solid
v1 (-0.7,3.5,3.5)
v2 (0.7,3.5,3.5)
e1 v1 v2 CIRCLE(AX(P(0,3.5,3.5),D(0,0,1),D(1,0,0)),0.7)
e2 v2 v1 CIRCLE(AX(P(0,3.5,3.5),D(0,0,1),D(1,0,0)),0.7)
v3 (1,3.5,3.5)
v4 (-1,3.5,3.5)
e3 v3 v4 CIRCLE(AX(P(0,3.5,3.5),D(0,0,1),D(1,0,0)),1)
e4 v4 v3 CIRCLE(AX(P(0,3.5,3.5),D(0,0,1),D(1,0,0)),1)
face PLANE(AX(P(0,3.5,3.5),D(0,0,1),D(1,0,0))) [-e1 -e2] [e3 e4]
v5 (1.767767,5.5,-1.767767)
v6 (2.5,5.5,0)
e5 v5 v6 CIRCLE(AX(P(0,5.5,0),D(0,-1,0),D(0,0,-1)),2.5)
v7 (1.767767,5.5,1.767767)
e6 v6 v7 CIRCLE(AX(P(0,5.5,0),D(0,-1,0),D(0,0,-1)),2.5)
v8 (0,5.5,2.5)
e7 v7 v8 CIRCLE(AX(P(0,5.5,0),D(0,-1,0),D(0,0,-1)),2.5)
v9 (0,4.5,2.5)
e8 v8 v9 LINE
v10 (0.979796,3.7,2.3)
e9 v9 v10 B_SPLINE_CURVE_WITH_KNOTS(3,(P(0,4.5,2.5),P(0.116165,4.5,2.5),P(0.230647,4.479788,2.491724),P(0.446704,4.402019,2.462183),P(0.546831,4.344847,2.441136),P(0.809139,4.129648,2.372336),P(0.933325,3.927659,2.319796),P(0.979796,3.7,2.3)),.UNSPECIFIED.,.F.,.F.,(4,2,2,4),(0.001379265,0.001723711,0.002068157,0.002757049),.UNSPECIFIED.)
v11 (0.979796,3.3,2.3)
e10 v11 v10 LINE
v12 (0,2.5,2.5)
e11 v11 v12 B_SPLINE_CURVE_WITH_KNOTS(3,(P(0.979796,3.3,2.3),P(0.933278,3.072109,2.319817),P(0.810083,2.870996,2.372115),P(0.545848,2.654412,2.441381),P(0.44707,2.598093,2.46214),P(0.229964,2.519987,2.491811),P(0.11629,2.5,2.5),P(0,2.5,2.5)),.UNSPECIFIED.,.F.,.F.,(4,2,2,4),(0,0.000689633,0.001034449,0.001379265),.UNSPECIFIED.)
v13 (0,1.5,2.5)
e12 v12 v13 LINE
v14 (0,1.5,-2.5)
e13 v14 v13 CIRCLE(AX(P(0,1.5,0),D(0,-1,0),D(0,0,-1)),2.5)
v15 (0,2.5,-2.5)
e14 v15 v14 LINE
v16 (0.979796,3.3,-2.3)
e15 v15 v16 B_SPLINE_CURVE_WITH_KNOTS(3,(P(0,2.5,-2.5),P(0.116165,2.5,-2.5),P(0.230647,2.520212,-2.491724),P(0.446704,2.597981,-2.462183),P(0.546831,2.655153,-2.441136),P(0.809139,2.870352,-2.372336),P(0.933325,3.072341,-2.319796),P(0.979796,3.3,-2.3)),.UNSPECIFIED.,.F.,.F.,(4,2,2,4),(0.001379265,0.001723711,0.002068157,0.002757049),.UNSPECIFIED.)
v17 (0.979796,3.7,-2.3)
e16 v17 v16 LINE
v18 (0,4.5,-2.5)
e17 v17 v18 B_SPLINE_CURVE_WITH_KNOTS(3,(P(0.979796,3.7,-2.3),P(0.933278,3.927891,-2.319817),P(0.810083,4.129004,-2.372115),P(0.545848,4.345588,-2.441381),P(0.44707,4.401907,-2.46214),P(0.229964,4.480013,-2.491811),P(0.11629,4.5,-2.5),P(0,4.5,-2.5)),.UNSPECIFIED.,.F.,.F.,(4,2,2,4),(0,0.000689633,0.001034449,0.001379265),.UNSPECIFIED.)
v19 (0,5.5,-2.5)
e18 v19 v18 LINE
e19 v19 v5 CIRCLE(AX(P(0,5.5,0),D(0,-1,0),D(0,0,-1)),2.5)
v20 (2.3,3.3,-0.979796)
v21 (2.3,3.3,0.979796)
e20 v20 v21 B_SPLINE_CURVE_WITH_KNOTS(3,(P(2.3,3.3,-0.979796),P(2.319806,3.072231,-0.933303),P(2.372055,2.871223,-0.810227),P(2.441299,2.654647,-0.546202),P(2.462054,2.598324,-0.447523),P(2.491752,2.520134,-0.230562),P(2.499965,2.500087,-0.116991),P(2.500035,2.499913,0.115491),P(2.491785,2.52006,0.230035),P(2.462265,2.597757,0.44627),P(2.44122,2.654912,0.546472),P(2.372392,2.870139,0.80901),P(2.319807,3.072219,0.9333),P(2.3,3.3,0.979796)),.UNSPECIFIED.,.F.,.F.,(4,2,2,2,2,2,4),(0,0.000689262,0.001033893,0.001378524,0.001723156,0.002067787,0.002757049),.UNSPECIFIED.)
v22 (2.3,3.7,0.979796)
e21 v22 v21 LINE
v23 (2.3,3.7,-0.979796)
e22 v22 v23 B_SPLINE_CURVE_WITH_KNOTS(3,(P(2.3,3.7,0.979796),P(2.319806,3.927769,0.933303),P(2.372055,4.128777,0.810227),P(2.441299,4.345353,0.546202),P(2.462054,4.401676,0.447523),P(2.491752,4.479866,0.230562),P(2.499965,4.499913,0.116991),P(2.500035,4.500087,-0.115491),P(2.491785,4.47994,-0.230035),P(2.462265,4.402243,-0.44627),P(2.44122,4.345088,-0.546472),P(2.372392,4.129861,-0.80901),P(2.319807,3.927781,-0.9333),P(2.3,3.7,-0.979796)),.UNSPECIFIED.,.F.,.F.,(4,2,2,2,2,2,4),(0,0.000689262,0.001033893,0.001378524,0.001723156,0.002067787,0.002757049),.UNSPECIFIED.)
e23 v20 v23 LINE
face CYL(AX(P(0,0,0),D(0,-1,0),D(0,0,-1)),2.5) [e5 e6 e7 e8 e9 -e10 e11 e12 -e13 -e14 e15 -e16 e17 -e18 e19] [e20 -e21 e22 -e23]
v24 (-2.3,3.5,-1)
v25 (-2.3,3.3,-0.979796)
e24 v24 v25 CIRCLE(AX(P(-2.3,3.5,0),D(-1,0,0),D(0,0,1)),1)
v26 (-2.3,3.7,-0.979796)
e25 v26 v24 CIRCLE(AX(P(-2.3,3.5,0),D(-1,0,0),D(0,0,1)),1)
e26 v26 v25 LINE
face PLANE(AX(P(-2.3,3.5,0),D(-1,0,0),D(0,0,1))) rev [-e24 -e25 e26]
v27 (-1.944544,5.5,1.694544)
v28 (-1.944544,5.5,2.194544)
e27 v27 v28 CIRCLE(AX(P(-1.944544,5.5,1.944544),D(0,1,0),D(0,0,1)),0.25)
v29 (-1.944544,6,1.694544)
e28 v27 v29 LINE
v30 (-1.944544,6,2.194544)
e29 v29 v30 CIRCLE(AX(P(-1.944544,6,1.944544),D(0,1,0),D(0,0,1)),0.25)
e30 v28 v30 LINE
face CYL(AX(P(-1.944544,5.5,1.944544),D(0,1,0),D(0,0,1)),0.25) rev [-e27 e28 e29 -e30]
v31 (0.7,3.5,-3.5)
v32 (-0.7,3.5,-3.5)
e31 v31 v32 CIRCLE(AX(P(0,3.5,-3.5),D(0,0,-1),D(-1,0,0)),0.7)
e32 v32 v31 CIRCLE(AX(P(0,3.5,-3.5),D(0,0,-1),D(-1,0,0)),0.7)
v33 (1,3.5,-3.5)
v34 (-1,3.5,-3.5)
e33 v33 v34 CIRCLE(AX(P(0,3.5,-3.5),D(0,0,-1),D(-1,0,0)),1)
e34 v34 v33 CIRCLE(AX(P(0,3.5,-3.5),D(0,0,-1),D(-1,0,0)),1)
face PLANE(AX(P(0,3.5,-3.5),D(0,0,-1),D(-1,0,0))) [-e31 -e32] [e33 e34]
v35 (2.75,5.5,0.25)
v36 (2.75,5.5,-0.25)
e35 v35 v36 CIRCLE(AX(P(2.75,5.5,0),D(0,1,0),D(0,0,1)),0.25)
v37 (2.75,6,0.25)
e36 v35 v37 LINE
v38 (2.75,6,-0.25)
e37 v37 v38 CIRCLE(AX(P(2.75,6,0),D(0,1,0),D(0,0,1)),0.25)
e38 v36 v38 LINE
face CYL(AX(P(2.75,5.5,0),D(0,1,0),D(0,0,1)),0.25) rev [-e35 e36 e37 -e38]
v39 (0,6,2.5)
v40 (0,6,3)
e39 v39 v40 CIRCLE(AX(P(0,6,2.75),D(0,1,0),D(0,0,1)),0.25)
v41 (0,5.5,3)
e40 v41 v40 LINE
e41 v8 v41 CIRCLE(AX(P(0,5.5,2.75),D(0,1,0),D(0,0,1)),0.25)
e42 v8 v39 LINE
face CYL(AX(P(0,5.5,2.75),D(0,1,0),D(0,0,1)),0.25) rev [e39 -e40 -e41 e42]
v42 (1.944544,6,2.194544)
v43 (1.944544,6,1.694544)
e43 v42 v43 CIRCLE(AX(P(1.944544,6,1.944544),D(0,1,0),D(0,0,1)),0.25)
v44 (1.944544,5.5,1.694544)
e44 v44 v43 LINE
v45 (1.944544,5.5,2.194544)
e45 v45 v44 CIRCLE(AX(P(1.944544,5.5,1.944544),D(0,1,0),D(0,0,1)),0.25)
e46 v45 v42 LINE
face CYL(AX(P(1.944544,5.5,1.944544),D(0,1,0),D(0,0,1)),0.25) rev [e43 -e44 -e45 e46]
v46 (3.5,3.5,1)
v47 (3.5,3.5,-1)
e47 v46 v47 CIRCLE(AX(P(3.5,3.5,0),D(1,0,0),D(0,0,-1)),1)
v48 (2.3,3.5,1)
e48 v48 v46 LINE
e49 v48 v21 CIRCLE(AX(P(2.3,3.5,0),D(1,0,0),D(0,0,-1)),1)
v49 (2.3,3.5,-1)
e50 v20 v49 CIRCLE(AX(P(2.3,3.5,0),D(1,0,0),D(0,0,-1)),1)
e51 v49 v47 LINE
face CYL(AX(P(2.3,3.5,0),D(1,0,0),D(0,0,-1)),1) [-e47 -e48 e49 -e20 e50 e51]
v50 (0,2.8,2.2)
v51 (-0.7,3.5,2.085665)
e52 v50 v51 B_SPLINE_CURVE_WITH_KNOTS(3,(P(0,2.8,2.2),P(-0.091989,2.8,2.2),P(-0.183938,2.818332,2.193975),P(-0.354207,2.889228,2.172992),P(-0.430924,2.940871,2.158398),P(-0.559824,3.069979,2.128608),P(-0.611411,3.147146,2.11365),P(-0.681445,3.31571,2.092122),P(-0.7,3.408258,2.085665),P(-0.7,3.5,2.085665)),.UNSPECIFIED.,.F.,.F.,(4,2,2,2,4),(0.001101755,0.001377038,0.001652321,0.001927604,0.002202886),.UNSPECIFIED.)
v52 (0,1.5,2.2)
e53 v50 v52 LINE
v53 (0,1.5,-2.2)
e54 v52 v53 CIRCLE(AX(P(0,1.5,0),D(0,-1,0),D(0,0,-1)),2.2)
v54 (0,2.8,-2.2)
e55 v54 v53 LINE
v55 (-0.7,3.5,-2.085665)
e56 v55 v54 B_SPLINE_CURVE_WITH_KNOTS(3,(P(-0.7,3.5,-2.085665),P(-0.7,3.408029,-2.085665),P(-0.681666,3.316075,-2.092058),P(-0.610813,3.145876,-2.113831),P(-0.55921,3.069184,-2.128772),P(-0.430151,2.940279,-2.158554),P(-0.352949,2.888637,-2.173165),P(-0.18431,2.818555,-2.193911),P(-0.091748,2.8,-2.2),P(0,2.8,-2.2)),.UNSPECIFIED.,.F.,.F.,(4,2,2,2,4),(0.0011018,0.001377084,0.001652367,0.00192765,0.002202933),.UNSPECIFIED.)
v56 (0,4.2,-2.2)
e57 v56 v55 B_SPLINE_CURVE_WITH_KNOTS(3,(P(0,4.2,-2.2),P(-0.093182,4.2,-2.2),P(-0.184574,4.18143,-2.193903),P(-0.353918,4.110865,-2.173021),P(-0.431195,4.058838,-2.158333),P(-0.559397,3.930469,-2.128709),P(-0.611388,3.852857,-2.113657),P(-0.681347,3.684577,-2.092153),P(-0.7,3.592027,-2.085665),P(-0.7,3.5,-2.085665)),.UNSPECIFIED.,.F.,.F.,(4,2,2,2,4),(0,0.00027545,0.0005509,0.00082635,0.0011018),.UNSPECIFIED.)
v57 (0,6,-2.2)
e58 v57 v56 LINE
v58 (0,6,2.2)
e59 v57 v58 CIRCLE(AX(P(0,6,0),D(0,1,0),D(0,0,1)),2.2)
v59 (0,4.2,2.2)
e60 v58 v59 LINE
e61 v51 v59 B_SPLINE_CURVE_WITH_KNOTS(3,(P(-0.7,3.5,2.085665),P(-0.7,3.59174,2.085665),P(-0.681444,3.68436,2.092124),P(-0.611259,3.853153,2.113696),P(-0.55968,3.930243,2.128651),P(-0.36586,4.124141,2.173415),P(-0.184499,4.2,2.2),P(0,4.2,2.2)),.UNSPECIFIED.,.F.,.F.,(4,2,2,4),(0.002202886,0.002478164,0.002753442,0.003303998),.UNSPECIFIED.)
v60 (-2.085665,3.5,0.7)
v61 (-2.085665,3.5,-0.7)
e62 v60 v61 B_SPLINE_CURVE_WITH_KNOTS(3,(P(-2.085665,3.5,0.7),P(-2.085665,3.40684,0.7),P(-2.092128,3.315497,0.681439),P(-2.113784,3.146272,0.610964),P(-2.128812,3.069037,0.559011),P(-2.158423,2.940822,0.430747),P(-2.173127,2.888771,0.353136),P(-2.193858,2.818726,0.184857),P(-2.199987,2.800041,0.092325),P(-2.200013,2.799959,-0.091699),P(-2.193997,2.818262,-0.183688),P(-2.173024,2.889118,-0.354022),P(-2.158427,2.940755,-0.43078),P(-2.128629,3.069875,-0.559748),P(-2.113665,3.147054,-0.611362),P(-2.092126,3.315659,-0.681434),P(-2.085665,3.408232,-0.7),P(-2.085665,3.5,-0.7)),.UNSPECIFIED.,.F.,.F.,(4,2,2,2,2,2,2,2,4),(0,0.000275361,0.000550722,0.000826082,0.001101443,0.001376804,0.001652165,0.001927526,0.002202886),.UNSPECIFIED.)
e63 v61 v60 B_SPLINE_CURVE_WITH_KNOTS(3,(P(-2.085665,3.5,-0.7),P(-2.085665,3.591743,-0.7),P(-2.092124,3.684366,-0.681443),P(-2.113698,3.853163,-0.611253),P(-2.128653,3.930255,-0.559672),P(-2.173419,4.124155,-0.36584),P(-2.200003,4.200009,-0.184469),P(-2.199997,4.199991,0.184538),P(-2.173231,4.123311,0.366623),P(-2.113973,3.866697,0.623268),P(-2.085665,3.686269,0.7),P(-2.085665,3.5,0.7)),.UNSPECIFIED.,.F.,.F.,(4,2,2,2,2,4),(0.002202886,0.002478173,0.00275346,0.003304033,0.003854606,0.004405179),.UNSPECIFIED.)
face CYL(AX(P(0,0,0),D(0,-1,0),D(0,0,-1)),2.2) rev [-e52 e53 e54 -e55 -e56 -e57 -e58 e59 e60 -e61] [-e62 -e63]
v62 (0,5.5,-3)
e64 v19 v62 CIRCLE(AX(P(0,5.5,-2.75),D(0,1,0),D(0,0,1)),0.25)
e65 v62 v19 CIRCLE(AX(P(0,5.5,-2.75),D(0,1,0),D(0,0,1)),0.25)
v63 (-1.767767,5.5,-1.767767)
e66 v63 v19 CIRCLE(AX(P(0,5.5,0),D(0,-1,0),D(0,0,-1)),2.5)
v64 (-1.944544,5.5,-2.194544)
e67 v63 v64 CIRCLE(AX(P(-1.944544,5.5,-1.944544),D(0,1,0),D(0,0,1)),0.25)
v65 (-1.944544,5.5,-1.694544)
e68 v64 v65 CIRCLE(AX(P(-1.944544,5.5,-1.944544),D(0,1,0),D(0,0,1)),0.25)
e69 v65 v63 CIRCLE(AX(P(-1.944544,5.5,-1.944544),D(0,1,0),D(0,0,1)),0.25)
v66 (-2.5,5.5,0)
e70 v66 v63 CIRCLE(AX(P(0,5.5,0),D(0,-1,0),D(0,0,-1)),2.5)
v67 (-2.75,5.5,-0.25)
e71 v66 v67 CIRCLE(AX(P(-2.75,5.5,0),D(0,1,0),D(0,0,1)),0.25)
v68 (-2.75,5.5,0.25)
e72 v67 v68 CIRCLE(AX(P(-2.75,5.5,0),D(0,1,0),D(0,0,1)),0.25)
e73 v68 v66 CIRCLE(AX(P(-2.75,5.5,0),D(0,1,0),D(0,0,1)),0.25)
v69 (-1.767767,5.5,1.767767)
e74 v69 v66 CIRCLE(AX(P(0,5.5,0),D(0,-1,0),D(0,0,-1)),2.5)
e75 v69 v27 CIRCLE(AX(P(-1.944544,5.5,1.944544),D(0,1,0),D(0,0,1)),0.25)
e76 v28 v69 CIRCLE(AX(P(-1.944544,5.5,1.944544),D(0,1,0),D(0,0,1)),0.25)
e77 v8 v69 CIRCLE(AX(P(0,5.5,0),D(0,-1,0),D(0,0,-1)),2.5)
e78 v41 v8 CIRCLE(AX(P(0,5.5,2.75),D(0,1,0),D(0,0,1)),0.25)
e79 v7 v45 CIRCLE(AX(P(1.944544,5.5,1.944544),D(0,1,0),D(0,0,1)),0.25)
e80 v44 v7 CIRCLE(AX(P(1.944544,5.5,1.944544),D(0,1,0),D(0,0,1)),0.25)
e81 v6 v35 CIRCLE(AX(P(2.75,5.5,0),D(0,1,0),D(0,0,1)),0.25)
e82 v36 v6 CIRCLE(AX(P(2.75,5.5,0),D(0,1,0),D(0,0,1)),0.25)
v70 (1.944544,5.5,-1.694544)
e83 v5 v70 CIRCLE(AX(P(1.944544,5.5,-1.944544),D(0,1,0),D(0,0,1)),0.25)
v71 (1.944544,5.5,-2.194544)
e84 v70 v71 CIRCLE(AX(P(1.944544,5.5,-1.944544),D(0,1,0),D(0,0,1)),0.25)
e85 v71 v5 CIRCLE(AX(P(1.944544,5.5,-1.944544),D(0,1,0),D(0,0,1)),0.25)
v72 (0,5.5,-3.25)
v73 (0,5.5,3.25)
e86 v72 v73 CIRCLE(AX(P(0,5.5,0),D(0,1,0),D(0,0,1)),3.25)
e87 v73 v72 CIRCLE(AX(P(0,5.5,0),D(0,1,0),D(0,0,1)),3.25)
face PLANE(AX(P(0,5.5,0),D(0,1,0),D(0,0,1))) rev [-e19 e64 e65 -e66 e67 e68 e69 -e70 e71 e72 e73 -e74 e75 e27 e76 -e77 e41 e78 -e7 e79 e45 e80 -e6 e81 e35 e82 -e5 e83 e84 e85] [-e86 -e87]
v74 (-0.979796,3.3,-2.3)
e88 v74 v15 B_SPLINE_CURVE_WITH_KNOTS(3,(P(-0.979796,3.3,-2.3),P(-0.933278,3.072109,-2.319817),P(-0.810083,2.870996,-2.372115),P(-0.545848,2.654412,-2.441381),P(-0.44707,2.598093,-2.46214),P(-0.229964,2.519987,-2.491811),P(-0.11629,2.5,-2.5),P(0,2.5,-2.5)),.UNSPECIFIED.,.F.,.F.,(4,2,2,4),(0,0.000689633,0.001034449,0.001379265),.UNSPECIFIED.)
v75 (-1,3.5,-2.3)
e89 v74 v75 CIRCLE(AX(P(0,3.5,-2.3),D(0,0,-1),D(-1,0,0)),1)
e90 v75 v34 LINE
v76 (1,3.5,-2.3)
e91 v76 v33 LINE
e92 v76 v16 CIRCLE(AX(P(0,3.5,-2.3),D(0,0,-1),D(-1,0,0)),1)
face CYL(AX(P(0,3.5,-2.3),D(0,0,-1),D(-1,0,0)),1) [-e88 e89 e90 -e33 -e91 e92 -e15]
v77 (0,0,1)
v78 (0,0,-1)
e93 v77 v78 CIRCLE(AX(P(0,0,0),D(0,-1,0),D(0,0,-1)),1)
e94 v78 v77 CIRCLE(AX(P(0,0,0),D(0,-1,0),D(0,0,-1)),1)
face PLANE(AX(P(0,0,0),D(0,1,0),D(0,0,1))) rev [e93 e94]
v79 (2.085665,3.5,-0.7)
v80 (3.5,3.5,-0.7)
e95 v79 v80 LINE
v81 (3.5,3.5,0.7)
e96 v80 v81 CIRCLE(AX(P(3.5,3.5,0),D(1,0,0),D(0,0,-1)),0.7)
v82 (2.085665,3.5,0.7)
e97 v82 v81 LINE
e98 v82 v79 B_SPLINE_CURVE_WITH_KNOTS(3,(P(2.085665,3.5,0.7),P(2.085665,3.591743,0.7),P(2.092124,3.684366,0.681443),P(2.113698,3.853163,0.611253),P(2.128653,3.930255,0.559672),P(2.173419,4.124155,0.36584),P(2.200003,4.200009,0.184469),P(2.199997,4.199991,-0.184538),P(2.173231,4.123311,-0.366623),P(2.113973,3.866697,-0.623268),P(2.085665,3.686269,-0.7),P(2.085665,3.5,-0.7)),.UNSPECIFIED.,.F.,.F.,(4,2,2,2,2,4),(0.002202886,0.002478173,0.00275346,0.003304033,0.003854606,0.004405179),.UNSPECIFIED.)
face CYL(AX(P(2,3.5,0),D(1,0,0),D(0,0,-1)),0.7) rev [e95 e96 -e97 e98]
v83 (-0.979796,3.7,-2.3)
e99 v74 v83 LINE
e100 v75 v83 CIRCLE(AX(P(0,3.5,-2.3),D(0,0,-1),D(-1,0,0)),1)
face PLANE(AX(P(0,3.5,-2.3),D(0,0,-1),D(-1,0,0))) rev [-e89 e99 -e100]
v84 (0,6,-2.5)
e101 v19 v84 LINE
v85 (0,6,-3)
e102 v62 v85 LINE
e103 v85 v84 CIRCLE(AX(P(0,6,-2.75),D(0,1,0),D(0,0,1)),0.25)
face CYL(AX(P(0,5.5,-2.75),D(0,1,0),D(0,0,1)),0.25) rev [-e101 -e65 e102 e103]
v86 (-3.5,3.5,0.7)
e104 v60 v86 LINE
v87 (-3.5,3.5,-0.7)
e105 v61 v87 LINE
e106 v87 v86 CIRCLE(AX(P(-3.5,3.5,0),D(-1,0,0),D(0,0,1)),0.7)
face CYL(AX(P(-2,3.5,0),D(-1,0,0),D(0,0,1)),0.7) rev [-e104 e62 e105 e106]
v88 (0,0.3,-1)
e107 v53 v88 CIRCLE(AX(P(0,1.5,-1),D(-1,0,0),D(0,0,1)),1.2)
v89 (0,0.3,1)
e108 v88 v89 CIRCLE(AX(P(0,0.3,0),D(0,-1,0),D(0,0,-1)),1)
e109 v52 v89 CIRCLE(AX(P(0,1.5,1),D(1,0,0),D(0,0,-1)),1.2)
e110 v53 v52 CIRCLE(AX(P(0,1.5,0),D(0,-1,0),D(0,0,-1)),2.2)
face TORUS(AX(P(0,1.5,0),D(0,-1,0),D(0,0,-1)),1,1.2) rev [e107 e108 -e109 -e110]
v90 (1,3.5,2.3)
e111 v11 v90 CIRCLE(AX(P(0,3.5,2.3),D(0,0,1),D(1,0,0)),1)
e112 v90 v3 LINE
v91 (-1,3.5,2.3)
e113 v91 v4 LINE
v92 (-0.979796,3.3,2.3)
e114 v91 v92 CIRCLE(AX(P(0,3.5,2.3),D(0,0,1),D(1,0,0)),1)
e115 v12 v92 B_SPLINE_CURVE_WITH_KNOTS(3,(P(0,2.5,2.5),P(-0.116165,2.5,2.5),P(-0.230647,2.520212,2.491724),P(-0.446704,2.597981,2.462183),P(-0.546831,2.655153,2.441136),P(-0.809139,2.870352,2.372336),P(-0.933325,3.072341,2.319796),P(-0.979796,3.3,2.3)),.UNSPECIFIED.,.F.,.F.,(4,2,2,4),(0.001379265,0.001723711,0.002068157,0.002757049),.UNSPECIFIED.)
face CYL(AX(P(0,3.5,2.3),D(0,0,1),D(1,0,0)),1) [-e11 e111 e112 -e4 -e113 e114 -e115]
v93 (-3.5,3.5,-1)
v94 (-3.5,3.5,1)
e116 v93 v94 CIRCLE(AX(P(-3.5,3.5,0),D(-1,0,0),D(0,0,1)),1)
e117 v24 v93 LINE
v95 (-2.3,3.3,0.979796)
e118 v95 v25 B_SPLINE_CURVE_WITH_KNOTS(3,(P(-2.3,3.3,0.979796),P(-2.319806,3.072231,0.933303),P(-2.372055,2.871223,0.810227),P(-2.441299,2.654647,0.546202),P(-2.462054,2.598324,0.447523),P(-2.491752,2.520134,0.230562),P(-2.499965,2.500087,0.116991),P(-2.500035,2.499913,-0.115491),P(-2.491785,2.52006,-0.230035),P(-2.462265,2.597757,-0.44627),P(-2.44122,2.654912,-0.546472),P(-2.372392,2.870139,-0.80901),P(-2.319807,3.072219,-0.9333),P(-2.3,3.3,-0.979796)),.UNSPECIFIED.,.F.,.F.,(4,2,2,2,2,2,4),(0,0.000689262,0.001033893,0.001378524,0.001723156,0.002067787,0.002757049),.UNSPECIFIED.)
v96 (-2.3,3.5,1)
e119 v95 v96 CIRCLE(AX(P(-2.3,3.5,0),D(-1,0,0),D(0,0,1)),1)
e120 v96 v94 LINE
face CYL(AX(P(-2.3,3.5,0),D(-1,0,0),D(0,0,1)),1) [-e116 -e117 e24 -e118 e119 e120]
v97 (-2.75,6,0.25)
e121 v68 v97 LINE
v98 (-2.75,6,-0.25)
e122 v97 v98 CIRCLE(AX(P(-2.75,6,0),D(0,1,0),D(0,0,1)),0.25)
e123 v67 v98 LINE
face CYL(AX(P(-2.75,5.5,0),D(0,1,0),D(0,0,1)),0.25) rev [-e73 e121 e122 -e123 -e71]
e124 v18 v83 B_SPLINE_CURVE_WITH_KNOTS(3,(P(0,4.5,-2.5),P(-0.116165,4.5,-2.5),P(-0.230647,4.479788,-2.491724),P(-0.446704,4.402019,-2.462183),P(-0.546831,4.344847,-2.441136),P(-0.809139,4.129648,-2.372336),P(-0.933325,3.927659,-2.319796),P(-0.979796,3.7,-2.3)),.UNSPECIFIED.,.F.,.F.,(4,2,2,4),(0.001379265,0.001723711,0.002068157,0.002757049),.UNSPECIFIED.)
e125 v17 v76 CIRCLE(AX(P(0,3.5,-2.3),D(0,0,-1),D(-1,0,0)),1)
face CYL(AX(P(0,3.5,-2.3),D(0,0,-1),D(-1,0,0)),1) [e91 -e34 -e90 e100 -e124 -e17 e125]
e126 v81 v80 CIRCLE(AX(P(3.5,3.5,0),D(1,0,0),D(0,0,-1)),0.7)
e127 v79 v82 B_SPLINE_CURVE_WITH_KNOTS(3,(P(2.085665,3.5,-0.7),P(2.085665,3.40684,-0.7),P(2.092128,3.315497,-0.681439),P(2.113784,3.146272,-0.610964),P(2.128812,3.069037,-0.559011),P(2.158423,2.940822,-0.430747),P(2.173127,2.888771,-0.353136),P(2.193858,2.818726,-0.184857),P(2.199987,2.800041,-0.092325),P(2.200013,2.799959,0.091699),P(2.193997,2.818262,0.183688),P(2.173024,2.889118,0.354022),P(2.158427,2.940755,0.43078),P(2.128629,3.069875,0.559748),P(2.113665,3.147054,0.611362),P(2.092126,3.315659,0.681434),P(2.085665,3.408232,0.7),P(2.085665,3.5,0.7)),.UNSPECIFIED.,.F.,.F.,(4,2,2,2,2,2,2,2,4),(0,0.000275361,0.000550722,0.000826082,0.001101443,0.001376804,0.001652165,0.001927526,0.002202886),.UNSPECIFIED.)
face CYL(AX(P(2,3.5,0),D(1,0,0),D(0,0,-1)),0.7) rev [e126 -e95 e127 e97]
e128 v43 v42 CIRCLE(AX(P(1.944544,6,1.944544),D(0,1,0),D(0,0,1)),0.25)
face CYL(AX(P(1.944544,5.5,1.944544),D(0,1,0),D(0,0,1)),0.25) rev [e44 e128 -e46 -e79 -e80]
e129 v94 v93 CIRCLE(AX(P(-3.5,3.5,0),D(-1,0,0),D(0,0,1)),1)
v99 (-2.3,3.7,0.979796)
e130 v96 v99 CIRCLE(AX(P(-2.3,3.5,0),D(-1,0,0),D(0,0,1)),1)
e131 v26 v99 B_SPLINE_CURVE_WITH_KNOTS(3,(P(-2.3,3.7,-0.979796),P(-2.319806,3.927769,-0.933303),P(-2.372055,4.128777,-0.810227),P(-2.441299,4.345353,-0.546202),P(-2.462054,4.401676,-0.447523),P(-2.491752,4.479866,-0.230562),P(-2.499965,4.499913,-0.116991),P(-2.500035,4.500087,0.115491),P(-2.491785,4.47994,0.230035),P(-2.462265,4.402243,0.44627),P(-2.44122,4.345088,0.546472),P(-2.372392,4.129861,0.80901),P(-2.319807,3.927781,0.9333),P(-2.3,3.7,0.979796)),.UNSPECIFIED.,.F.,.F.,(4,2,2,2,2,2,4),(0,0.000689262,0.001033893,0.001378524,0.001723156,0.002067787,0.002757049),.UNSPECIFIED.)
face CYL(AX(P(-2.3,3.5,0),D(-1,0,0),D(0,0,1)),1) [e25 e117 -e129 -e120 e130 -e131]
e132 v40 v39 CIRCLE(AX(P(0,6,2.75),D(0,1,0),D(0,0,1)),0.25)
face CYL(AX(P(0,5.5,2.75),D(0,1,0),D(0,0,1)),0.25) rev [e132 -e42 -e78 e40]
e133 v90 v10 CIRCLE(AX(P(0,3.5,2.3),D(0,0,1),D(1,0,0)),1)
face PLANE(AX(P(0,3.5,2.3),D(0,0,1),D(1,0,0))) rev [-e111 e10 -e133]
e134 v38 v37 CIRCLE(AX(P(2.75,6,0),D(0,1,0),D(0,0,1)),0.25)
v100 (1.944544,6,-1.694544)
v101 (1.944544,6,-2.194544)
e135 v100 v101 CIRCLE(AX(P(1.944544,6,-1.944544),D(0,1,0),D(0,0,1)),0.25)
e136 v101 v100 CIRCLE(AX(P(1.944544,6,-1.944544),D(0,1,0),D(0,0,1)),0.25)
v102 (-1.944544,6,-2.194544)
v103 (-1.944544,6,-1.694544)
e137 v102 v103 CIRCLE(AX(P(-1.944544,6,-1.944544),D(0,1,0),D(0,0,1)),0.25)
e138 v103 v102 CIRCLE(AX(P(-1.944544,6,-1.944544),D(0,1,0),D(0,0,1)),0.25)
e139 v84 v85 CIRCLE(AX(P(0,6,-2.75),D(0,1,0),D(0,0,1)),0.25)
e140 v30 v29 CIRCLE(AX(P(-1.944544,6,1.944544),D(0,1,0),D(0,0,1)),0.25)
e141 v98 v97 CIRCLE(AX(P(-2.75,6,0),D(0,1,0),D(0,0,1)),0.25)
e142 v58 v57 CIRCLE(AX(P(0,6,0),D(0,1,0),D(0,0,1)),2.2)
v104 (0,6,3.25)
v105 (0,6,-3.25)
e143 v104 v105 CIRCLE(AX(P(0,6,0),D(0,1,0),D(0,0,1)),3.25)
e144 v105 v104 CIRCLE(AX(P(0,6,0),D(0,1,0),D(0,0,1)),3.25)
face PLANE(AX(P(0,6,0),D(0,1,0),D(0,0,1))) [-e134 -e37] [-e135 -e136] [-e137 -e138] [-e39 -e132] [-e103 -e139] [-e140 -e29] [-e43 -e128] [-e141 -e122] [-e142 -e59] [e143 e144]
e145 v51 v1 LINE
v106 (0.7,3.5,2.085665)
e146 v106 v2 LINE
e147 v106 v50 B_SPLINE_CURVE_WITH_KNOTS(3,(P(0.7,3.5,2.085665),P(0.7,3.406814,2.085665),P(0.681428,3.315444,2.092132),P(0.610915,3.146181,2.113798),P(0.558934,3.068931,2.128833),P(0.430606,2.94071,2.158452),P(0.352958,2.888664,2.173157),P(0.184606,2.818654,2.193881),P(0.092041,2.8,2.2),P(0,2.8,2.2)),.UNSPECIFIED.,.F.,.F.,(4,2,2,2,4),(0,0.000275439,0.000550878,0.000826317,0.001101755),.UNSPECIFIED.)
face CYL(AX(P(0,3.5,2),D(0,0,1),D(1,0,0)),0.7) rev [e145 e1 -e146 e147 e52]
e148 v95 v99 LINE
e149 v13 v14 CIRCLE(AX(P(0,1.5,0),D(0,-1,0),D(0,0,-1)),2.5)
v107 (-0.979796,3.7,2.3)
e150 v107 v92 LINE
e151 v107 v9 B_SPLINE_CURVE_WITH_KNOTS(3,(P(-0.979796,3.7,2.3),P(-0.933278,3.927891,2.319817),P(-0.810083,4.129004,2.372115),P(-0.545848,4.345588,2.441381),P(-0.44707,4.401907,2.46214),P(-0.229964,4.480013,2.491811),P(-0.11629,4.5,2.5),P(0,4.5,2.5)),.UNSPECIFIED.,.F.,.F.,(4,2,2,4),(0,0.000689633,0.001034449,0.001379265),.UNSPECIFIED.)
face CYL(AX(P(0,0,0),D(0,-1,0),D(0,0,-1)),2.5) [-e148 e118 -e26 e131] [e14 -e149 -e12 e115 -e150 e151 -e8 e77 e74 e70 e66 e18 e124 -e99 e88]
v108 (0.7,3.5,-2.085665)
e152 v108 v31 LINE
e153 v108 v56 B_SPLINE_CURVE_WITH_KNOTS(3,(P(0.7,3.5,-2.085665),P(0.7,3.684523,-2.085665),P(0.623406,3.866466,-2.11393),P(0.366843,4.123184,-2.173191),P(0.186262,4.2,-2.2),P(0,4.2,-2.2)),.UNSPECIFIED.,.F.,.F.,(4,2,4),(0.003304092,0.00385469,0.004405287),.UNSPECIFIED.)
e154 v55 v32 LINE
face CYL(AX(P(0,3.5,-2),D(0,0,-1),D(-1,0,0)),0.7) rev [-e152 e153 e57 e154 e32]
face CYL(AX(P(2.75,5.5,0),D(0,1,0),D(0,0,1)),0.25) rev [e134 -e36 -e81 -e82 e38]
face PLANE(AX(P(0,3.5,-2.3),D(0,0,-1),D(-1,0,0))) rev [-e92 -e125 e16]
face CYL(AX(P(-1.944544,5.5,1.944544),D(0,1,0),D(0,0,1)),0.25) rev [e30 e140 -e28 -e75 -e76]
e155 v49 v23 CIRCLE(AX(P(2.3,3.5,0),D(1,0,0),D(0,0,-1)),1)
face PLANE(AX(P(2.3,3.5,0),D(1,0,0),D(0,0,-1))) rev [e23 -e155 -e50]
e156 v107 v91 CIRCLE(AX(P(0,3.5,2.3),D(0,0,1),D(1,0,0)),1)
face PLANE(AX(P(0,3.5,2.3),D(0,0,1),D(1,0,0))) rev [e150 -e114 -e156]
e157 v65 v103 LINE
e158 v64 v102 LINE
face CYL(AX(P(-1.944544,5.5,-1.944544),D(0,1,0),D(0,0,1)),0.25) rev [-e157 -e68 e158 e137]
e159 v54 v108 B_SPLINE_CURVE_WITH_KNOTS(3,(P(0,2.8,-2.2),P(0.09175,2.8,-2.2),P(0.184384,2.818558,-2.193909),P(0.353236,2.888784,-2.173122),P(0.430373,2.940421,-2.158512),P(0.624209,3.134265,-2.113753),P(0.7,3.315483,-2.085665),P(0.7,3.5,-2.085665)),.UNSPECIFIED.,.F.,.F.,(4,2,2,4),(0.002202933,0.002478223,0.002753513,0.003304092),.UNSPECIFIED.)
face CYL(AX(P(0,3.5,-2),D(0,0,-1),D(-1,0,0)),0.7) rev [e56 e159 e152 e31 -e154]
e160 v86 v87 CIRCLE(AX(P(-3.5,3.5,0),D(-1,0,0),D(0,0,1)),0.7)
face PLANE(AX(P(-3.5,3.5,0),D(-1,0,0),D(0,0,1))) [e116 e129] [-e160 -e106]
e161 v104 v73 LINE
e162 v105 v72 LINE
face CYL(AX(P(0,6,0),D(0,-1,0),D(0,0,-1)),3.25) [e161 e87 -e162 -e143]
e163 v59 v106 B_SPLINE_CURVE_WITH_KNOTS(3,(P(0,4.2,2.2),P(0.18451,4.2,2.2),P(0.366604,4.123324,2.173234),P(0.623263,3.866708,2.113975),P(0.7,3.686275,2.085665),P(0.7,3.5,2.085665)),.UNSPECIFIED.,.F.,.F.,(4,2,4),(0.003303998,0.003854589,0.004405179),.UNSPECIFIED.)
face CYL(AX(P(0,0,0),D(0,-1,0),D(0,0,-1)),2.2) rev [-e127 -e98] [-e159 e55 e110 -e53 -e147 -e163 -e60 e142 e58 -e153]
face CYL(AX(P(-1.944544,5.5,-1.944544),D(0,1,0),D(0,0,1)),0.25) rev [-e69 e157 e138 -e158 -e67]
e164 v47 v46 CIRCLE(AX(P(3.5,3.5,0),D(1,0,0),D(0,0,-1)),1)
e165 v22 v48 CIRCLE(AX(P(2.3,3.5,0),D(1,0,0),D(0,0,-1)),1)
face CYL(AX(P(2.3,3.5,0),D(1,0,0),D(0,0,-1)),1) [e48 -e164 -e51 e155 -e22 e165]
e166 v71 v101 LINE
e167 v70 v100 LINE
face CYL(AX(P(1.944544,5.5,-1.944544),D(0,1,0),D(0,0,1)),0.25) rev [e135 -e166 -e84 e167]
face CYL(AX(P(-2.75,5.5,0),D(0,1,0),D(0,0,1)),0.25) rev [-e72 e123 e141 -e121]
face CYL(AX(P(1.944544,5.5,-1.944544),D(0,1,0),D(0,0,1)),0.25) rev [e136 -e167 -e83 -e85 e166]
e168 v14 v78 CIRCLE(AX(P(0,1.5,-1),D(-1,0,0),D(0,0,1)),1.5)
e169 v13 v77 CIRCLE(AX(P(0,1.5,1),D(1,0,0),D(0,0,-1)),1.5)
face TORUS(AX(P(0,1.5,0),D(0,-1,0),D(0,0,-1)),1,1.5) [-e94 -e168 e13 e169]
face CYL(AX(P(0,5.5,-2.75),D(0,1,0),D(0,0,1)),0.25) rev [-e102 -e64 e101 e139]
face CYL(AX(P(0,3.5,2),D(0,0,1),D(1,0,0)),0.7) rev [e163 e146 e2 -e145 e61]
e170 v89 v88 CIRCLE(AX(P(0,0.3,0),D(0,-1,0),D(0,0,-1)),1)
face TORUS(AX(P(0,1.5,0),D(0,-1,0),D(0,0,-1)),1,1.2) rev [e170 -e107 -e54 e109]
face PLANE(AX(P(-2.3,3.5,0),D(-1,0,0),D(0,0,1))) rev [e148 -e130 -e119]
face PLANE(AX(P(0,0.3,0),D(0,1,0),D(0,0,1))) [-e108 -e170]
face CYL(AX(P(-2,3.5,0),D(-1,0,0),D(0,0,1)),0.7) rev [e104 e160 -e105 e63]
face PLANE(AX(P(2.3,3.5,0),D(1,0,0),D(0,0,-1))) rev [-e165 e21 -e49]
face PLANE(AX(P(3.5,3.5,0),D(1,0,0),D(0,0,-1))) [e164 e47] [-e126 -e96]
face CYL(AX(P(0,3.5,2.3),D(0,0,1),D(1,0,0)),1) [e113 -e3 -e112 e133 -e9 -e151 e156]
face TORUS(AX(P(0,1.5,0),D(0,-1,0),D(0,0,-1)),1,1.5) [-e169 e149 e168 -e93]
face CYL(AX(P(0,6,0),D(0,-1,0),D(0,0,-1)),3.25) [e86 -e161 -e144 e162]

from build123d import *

# Parameters (mm, degrees)
BODY_SHELL_0_3_T            = -0.3
FLANGE_SKETCH_6_5_R         = 3.25
FLANGE_DEPTH                = 0.5
FLANGE_START                = -0.5
FLANGE_BORE_SKETCH_R        = 2.2
FLANGE_BORE_DEPTH           = 0.5
FLANGE_BOLT_HOLES_SKETCH_R  = 0.25
FLANGE_BOLT_HOLES_8X_DEPTH  = 0.5
SIDE_PORT_BOSS_SKETCH_2_R   = 1
SIDE_PORT_BOSS_DEPTH        = 1.2
SIDE_PORT_BORE_SKETCH_1_4_R = 0.7
SIDE_PORT_BORE_1_4_DEPTH    = 1.5
SIDE_PORT_PATTERN_4X_COUNT  = 4


with BuildPart() as part:
    # Body Profile Sketch → Body Revolve (revolve)
    with BuildSketch(Plane.XY, mode=Mode.PRIVATE) as body_revolve_sk:
        with BuildLine():
            Line((0, 0), (0, 5.5))
            Line((0, 5.5), (-2.5, 5.5))
            Line((-2.5, 5.5), (-2.5, 1.5))
            ThreePointArc((-2.5, 1.5), (-2.060660172, 0.439339828), (-1, 0))
            Line((-1, 0), (0, 0))
        make_face()
    revolve(body_revolve_sk.sketch.rotate(Axis((0, 0, 0), (0, 1, 0)), 270), axis=Axis((0, 0, 0), (0, 1, 0)))

    # Body Shell 0.3
    body_shell_0_3_openings = [part.faces().sort_by_distance(p)[0] for p in [
        (0, 5.5, 0),
    ]]
    offset(amount=BODY_SHELL_0_3_T, openings=body_shell_0_3_openings, kind=Kind.INTERSECTION)

    # Flange Sketch Ø6.5 → Flange (add)
    with BuildSketch(Plane(origin=(0, 5.5, 0), x_dir=(1, 0, 0), z_dir=(0, 1, 0))):
        with Locations(Location((0, 0, 0), (0, 0, 270))):
            Circle(FLANGE_SKETCH_6_5_R)
    extrude(amount=FLANGE_DEPTH)

    # Flange Bore Sketch → Flange Bore (cut)
    with BuildSketch(Plane(origin=(0, 6, 0), x_dir=(1, 0, 0), z_dir=(0, 1, 0)).offset(FLANGE_START)):
        with Locations(Location((0, 0, 0), (0, 0, 90))):
            Circle(FLANGE_BORE_SKETCH_R)
    extrude(amount=FLANGE_BORE_DEPTH, mode=Mode.SUBTRACT)

    # Flange Bolt Holes Sketch → Flange Bolt Holes 8x (cut)
    with BuildSketch(Plane(origin=(0, 6, 0), x_dir=(1, 0, 0), z_dir=(0, 1, 0))):
        with Locations(Location((0, 2.75, 0), (0, 0, 270))):
            Circle(FLANGE_BOLT_HOLES_SKETCH_R)
        with Locations(Location((1.944543648, 1.944543648, 0), (0, 0, 270))):
            Circle(FLANGE_BOLT_HOLES_SKETCH_R)
        with Locations(Location((2.75, 0, 0), (0, 0, 270))):
            Circle(FLANGE_BOLT_HOLES_SKETCH_R)
        with Locations(Location((1.944543648, -1.944543648, 0), (0, 0, 270))):
            Circle(FLANGE_BOLT_HOLES_SKETCH_R)
        with Locations(Location((0, -2.75, 0), (0, 0, 270))):
            Circle(FLANGE_BOLT_HOLES_SKETCH_R)
        with Locations(Location((-1.944543648, -1.944543648, 0), (0, 0, 270))):
            Circle(FLANGE_BOLT_HOLES_SKETCH_R)
        with Locations(Location((-2.75, 0, 0), (0, 0, 270))):
            Circle(FLANGE_BOLT_HOLES_SKETCH_R)
        with Locations(Location((-1.944543648, 1.944543648, 0), (0, 0, 270))):
            Circle(FLANGE_BOLT_HOLES_SKETCH_R)
    extrude(amount=-FLANGE_BOLT_HOLES_8X_DEPTH, mode=Mode.SUBTRACT)

    # Side Port Boss Sketch Ø2 → Side Port Boss (add)
    with BuildSketch(Plane.XY.offset(3.5)):
        with Locations((0, 3.5)):
            Circle(SIDE_PORT_BOSS_SKETCH_2_R)
    side_port_boss = extrude(amount=-SIDE_PORT_BOSS_DEPTH)

    # Side Port Bore Sketch Ø1.4 → Side Port Bore Ø1.4 (cut)
    with BuildSketch(Plane.XY.offset(3.5)):
        with Locations((0, 3.5)):
            Circle(SIDE_PORT_BORE_SKETCH_1_4_R)
    side_port_bore_1_4 = extrude(amount=-SIDE_PORT_BORE_1_4_DEPTH, mode=Mode.SUBTRACT)

    # Side Port Pattern 4x: Side Port Boss, Side Port Bore Ø1.4 ×4 about axis
    side_port_pattern_4x_axis = Axis((0, 0, 0), (0, 1, 0))
    add([side_port_boss.rotate(side_port_pattern_4x_axis, i * 360 / SIDE_PORT_PATTERN_4X_COUNT) for i in range(1, SIDE_PORT_PATTERN_4X_COUNT)])
    add([side_port_bore_1_4.rotate(side_port_pattern_4x_axis, i * 360 / SIDE_PORT_PATTERN_4X_COUNT) for i in range(1, SIDE_PORT_PATTERN_4X_COUNT)], mode=Mode.SUBTRACT)


solid = part.part
